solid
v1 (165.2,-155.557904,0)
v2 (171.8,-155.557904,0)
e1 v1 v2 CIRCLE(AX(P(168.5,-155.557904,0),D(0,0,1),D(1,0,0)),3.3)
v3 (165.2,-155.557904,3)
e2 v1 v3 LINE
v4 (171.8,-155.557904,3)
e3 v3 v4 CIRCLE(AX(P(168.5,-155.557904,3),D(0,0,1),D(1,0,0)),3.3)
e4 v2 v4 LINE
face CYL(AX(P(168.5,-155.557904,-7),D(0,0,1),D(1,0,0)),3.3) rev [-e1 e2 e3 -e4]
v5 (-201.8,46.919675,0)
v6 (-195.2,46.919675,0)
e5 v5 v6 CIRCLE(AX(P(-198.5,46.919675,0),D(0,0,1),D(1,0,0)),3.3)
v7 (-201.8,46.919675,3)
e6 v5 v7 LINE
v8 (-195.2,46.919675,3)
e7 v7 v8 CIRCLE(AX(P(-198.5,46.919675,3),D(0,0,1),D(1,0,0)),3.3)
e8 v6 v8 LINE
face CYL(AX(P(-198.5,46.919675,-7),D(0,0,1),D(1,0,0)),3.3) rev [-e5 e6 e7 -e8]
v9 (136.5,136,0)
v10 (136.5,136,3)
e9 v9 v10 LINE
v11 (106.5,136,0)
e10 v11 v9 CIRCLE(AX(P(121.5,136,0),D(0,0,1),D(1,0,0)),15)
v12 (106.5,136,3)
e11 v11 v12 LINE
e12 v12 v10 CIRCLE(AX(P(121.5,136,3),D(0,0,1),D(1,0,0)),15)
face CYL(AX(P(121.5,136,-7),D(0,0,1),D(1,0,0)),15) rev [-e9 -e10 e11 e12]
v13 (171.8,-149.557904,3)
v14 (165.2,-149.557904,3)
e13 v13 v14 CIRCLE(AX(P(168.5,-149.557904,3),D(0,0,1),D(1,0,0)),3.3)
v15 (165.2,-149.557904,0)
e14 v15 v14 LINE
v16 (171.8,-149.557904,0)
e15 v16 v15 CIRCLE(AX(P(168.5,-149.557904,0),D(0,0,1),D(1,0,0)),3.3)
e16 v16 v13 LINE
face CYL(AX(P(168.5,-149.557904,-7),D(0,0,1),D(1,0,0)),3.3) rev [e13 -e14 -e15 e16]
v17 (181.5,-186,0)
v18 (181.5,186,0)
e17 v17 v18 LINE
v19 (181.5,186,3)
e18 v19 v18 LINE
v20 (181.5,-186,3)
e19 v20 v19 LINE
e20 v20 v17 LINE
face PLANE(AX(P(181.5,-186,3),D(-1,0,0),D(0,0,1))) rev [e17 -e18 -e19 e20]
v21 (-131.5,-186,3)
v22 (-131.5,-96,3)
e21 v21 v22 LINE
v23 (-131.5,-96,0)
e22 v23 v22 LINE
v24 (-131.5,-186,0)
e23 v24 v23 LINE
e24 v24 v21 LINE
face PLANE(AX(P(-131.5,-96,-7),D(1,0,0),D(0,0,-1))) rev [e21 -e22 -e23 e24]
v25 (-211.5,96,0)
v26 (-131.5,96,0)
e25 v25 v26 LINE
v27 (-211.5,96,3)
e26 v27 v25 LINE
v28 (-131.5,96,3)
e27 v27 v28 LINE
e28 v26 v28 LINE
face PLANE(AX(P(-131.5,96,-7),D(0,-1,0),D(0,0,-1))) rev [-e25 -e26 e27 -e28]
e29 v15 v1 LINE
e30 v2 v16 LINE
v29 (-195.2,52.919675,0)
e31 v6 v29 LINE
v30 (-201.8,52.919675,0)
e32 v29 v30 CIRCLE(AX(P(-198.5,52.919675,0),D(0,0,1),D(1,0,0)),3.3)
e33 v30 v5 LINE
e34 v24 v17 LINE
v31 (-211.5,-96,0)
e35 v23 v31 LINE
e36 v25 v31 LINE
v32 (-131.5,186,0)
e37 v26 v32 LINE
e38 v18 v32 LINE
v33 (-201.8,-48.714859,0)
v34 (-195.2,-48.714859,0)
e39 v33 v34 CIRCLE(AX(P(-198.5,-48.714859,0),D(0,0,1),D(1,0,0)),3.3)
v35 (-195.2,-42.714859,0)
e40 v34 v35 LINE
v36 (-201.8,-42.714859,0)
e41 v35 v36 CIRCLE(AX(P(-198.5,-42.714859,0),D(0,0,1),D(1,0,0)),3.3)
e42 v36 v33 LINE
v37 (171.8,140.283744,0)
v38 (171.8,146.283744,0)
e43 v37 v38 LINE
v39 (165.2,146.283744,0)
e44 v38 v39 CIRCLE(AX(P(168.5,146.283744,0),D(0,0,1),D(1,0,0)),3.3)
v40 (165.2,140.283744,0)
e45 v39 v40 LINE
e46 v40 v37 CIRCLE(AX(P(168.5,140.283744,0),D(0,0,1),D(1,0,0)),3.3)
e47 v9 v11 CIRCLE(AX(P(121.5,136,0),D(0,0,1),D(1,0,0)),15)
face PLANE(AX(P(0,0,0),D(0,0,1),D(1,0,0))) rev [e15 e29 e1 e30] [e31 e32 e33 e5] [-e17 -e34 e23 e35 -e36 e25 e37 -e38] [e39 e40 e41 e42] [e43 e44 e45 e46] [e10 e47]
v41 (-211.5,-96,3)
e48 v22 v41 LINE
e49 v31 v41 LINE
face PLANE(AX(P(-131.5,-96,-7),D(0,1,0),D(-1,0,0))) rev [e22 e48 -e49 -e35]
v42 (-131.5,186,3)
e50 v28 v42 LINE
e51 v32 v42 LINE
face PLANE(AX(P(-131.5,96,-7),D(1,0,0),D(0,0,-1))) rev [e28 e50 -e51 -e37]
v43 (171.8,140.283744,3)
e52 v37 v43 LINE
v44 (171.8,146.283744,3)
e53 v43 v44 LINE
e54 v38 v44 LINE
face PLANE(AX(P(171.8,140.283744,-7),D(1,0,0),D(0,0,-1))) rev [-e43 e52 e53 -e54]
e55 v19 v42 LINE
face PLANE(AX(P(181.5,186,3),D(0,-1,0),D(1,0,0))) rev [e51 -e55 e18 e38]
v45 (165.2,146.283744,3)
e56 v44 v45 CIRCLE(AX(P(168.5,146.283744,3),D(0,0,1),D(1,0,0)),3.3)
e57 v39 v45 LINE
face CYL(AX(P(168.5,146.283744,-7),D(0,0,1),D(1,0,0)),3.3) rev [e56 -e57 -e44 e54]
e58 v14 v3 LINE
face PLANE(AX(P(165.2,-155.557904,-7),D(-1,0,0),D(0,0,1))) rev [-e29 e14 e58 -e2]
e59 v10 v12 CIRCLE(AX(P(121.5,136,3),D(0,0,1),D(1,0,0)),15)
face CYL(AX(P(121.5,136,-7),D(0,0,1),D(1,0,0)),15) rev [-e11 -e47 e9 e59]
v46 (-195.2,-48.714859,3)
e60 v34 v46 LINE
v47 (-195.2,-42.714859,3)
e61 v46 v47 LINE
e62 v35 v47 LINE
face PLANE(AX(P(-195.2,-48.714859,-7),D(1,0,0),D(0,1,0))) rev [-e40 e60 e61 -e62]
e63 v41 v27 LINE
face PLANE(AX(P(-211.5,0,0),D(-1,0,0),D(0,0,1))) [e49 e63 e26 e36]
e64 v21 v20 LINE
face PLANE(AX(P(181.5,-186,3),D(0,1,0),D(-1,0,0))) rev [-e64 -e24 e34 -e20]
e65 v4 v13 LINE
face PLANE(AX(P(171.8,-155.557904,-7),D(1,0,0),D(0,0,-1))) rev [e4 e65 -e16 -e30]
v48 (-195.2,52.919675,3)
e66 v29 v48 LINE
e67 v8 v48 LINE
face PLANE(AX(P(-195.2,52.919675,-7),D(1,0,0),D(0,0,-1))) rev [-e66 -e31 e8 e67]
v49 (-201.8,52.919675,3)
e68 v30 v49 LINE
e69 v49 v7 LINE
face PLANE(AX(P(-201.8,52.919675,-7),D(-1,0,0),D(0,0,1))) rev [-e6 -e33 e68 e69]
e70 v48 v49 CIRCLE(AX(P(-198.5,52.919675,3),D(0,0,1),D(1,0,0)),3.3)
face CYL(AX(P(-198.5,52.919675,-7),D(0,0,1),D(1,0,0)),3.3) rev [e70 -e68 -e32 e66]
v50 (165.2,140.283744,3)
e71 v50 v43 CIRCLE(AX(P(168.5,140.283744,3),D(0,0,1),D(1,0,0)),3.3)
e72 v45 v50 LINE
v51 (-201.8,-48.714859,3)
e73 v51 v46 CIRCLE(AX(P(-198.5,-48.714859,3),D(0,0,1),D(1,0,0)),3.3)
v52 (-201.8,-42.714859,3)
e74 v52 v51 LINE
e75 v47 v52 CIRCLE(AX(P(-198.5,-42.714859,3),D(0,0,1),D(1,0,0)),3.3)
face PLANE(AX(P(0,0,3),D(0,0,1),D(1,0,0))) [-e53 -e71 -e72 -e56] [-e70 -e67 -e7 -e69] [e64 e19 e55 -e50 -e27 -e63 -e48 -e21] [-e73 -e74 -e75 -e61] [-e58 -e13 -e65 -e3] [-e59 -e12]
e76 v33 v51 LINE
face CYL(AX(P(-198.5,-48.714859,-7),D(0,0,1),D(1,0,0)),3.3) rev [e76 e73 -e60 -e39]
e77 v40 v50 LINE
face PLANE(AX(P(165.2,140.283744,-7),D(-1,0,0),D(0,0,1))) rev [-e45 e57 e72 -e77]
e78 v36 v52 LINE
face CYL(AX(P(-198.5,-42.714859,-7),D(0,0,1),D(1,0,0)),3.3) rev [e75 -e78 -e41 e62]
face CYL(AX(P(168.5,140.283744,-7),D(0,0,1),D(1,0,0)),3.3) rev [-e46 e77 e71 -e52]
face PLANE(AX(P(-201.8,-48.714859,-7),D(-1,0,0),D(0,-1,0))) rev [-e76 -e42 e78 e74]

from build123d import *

# Parameters (mm, degrees)
SKETCH_1_W          = 363
SKETCH_1_H          = 372
EXTRUDE_1_DEPTH     = 3
SKETCH_2_R          = 15
CUT_EXTRUDE_1_DEPTH = 10
SKETCH_3_W          = 50
SKETCH_3_H          = 90
CUT_EXTRUDE_2_DEPTH = 10
SKETCH_4_W          = 3
SKETCH_4_H          = 192
EXTRUDE_2_DEPTH     = 30
CUT_EXTRUDE_3_DEPTH = 10


with BuildPart() as part:
    # 草图1 → 凸台-拉伸1 (new body)
    with BuildSketch(Plane.XY):
        Rectangle(SKETCH_1_W, SKETCH_1_H)
    extrude(amount=EXTRUDE_1_DEPTH)

    # 草图2 → 切除-拉伸1 (cut)
    with BuildSketch(Plane.XY.offset(3)):
        with Locations((121.5, 136)):
            Circle(SKETCH_2_R)
    extrude(amount=-CUT_EXTRUDE_1_DEPTH, mode=Mode.SUBTRACT)

    # 草图3 → 切除-拉伸2 (cut)
    with BuildSketch(Plane.XY.offset(3)):
        with Locations((-156.5, -141)):
            Rectangle(SKETCH_3_W, SKETCH_3_H)
        with Locations((-156.5, 141)):
            Rectangle(SKETCH_3_W, SKETCH_3_H)
    extrude(amount=-CUT_EXTRUDE_2_DEPTH, mode=Mode.SUBTRACT)

    # 草图4 → 凸台-拉伸2 (add)
    with BuildSketch(Plane.ZY.offset(181.5)):
        with Locations((1.5, 0)):
            Rectangle(SKETCH_4_W, SKETCH_4_H)
    extrude(amount=EXTRUDE_2_DEPTH)

    # 草图5 → 切除-拉伸3 (cut)
    with BuildSketch(Plane.XY.offset(3)):
        with BuildLine():
            Line((165.2, -155.557904139), (165.2, -149.557904139))
            ThreePointArc((165.2, -149.557904139), (168.5, -146.257904139), (171.8, -149.557904139))
            Line((171.8, -149.557904139), (171.8, -155.557904139))
            ThreePointArc((171.8, -155.557904139), (168.5, -158.857904139), (165.2, -155.557904139))
        make_face()
        with BuildLine():
            Line((165.2, 140.283744441), (165.2, 146.283744441))
            ThreePointArc((165.2, 146.283744441), (168.5, 149.583744441), (171.8, 146.283744441))
            Line((171.8, 146.283744441), (171.8, 140.283744441))
            ThreePointArc((171.8, 140.283744441), (168.5, 136.983744441), (165.2, 140.283744441))
        make_face()
        with BuildLine():
            Line((-195.2, 52.919675482), (-195.2, 46.919675482))
            ThreePointArc((-195.2, 46.919675482), (-198.5, 43.619675482), (-201.8, 46.919675482))
            Line((-201.8, 46.919675482), (-201.8, 52.919675482))
            ThreePointArc((-201.8, 52.919675482), (-198.5, 56.219675482), (-195.2, 52.919675482))
        make_face()
        with BuildLine():
            Line((-201.8, -48.714858664), (-201.8, -42.714858664))
            ThreePointArc((-201.8, -42.714858664), (-198.5, -39.414858664), (-195.2, -42.714858664))
            Line((-195.2, -42.714858664), (-195.2, -48.714858664))
            ThreePointArc((-195.2, -48.714858664), (-198.5, -52.014858664), (-201.8, -48.714858664))
        make_face()
    extrude(amount=-CUT_EXTRUDE_3_DEPTH, mode=Mode.SUBTRACT)


solid = part.part
